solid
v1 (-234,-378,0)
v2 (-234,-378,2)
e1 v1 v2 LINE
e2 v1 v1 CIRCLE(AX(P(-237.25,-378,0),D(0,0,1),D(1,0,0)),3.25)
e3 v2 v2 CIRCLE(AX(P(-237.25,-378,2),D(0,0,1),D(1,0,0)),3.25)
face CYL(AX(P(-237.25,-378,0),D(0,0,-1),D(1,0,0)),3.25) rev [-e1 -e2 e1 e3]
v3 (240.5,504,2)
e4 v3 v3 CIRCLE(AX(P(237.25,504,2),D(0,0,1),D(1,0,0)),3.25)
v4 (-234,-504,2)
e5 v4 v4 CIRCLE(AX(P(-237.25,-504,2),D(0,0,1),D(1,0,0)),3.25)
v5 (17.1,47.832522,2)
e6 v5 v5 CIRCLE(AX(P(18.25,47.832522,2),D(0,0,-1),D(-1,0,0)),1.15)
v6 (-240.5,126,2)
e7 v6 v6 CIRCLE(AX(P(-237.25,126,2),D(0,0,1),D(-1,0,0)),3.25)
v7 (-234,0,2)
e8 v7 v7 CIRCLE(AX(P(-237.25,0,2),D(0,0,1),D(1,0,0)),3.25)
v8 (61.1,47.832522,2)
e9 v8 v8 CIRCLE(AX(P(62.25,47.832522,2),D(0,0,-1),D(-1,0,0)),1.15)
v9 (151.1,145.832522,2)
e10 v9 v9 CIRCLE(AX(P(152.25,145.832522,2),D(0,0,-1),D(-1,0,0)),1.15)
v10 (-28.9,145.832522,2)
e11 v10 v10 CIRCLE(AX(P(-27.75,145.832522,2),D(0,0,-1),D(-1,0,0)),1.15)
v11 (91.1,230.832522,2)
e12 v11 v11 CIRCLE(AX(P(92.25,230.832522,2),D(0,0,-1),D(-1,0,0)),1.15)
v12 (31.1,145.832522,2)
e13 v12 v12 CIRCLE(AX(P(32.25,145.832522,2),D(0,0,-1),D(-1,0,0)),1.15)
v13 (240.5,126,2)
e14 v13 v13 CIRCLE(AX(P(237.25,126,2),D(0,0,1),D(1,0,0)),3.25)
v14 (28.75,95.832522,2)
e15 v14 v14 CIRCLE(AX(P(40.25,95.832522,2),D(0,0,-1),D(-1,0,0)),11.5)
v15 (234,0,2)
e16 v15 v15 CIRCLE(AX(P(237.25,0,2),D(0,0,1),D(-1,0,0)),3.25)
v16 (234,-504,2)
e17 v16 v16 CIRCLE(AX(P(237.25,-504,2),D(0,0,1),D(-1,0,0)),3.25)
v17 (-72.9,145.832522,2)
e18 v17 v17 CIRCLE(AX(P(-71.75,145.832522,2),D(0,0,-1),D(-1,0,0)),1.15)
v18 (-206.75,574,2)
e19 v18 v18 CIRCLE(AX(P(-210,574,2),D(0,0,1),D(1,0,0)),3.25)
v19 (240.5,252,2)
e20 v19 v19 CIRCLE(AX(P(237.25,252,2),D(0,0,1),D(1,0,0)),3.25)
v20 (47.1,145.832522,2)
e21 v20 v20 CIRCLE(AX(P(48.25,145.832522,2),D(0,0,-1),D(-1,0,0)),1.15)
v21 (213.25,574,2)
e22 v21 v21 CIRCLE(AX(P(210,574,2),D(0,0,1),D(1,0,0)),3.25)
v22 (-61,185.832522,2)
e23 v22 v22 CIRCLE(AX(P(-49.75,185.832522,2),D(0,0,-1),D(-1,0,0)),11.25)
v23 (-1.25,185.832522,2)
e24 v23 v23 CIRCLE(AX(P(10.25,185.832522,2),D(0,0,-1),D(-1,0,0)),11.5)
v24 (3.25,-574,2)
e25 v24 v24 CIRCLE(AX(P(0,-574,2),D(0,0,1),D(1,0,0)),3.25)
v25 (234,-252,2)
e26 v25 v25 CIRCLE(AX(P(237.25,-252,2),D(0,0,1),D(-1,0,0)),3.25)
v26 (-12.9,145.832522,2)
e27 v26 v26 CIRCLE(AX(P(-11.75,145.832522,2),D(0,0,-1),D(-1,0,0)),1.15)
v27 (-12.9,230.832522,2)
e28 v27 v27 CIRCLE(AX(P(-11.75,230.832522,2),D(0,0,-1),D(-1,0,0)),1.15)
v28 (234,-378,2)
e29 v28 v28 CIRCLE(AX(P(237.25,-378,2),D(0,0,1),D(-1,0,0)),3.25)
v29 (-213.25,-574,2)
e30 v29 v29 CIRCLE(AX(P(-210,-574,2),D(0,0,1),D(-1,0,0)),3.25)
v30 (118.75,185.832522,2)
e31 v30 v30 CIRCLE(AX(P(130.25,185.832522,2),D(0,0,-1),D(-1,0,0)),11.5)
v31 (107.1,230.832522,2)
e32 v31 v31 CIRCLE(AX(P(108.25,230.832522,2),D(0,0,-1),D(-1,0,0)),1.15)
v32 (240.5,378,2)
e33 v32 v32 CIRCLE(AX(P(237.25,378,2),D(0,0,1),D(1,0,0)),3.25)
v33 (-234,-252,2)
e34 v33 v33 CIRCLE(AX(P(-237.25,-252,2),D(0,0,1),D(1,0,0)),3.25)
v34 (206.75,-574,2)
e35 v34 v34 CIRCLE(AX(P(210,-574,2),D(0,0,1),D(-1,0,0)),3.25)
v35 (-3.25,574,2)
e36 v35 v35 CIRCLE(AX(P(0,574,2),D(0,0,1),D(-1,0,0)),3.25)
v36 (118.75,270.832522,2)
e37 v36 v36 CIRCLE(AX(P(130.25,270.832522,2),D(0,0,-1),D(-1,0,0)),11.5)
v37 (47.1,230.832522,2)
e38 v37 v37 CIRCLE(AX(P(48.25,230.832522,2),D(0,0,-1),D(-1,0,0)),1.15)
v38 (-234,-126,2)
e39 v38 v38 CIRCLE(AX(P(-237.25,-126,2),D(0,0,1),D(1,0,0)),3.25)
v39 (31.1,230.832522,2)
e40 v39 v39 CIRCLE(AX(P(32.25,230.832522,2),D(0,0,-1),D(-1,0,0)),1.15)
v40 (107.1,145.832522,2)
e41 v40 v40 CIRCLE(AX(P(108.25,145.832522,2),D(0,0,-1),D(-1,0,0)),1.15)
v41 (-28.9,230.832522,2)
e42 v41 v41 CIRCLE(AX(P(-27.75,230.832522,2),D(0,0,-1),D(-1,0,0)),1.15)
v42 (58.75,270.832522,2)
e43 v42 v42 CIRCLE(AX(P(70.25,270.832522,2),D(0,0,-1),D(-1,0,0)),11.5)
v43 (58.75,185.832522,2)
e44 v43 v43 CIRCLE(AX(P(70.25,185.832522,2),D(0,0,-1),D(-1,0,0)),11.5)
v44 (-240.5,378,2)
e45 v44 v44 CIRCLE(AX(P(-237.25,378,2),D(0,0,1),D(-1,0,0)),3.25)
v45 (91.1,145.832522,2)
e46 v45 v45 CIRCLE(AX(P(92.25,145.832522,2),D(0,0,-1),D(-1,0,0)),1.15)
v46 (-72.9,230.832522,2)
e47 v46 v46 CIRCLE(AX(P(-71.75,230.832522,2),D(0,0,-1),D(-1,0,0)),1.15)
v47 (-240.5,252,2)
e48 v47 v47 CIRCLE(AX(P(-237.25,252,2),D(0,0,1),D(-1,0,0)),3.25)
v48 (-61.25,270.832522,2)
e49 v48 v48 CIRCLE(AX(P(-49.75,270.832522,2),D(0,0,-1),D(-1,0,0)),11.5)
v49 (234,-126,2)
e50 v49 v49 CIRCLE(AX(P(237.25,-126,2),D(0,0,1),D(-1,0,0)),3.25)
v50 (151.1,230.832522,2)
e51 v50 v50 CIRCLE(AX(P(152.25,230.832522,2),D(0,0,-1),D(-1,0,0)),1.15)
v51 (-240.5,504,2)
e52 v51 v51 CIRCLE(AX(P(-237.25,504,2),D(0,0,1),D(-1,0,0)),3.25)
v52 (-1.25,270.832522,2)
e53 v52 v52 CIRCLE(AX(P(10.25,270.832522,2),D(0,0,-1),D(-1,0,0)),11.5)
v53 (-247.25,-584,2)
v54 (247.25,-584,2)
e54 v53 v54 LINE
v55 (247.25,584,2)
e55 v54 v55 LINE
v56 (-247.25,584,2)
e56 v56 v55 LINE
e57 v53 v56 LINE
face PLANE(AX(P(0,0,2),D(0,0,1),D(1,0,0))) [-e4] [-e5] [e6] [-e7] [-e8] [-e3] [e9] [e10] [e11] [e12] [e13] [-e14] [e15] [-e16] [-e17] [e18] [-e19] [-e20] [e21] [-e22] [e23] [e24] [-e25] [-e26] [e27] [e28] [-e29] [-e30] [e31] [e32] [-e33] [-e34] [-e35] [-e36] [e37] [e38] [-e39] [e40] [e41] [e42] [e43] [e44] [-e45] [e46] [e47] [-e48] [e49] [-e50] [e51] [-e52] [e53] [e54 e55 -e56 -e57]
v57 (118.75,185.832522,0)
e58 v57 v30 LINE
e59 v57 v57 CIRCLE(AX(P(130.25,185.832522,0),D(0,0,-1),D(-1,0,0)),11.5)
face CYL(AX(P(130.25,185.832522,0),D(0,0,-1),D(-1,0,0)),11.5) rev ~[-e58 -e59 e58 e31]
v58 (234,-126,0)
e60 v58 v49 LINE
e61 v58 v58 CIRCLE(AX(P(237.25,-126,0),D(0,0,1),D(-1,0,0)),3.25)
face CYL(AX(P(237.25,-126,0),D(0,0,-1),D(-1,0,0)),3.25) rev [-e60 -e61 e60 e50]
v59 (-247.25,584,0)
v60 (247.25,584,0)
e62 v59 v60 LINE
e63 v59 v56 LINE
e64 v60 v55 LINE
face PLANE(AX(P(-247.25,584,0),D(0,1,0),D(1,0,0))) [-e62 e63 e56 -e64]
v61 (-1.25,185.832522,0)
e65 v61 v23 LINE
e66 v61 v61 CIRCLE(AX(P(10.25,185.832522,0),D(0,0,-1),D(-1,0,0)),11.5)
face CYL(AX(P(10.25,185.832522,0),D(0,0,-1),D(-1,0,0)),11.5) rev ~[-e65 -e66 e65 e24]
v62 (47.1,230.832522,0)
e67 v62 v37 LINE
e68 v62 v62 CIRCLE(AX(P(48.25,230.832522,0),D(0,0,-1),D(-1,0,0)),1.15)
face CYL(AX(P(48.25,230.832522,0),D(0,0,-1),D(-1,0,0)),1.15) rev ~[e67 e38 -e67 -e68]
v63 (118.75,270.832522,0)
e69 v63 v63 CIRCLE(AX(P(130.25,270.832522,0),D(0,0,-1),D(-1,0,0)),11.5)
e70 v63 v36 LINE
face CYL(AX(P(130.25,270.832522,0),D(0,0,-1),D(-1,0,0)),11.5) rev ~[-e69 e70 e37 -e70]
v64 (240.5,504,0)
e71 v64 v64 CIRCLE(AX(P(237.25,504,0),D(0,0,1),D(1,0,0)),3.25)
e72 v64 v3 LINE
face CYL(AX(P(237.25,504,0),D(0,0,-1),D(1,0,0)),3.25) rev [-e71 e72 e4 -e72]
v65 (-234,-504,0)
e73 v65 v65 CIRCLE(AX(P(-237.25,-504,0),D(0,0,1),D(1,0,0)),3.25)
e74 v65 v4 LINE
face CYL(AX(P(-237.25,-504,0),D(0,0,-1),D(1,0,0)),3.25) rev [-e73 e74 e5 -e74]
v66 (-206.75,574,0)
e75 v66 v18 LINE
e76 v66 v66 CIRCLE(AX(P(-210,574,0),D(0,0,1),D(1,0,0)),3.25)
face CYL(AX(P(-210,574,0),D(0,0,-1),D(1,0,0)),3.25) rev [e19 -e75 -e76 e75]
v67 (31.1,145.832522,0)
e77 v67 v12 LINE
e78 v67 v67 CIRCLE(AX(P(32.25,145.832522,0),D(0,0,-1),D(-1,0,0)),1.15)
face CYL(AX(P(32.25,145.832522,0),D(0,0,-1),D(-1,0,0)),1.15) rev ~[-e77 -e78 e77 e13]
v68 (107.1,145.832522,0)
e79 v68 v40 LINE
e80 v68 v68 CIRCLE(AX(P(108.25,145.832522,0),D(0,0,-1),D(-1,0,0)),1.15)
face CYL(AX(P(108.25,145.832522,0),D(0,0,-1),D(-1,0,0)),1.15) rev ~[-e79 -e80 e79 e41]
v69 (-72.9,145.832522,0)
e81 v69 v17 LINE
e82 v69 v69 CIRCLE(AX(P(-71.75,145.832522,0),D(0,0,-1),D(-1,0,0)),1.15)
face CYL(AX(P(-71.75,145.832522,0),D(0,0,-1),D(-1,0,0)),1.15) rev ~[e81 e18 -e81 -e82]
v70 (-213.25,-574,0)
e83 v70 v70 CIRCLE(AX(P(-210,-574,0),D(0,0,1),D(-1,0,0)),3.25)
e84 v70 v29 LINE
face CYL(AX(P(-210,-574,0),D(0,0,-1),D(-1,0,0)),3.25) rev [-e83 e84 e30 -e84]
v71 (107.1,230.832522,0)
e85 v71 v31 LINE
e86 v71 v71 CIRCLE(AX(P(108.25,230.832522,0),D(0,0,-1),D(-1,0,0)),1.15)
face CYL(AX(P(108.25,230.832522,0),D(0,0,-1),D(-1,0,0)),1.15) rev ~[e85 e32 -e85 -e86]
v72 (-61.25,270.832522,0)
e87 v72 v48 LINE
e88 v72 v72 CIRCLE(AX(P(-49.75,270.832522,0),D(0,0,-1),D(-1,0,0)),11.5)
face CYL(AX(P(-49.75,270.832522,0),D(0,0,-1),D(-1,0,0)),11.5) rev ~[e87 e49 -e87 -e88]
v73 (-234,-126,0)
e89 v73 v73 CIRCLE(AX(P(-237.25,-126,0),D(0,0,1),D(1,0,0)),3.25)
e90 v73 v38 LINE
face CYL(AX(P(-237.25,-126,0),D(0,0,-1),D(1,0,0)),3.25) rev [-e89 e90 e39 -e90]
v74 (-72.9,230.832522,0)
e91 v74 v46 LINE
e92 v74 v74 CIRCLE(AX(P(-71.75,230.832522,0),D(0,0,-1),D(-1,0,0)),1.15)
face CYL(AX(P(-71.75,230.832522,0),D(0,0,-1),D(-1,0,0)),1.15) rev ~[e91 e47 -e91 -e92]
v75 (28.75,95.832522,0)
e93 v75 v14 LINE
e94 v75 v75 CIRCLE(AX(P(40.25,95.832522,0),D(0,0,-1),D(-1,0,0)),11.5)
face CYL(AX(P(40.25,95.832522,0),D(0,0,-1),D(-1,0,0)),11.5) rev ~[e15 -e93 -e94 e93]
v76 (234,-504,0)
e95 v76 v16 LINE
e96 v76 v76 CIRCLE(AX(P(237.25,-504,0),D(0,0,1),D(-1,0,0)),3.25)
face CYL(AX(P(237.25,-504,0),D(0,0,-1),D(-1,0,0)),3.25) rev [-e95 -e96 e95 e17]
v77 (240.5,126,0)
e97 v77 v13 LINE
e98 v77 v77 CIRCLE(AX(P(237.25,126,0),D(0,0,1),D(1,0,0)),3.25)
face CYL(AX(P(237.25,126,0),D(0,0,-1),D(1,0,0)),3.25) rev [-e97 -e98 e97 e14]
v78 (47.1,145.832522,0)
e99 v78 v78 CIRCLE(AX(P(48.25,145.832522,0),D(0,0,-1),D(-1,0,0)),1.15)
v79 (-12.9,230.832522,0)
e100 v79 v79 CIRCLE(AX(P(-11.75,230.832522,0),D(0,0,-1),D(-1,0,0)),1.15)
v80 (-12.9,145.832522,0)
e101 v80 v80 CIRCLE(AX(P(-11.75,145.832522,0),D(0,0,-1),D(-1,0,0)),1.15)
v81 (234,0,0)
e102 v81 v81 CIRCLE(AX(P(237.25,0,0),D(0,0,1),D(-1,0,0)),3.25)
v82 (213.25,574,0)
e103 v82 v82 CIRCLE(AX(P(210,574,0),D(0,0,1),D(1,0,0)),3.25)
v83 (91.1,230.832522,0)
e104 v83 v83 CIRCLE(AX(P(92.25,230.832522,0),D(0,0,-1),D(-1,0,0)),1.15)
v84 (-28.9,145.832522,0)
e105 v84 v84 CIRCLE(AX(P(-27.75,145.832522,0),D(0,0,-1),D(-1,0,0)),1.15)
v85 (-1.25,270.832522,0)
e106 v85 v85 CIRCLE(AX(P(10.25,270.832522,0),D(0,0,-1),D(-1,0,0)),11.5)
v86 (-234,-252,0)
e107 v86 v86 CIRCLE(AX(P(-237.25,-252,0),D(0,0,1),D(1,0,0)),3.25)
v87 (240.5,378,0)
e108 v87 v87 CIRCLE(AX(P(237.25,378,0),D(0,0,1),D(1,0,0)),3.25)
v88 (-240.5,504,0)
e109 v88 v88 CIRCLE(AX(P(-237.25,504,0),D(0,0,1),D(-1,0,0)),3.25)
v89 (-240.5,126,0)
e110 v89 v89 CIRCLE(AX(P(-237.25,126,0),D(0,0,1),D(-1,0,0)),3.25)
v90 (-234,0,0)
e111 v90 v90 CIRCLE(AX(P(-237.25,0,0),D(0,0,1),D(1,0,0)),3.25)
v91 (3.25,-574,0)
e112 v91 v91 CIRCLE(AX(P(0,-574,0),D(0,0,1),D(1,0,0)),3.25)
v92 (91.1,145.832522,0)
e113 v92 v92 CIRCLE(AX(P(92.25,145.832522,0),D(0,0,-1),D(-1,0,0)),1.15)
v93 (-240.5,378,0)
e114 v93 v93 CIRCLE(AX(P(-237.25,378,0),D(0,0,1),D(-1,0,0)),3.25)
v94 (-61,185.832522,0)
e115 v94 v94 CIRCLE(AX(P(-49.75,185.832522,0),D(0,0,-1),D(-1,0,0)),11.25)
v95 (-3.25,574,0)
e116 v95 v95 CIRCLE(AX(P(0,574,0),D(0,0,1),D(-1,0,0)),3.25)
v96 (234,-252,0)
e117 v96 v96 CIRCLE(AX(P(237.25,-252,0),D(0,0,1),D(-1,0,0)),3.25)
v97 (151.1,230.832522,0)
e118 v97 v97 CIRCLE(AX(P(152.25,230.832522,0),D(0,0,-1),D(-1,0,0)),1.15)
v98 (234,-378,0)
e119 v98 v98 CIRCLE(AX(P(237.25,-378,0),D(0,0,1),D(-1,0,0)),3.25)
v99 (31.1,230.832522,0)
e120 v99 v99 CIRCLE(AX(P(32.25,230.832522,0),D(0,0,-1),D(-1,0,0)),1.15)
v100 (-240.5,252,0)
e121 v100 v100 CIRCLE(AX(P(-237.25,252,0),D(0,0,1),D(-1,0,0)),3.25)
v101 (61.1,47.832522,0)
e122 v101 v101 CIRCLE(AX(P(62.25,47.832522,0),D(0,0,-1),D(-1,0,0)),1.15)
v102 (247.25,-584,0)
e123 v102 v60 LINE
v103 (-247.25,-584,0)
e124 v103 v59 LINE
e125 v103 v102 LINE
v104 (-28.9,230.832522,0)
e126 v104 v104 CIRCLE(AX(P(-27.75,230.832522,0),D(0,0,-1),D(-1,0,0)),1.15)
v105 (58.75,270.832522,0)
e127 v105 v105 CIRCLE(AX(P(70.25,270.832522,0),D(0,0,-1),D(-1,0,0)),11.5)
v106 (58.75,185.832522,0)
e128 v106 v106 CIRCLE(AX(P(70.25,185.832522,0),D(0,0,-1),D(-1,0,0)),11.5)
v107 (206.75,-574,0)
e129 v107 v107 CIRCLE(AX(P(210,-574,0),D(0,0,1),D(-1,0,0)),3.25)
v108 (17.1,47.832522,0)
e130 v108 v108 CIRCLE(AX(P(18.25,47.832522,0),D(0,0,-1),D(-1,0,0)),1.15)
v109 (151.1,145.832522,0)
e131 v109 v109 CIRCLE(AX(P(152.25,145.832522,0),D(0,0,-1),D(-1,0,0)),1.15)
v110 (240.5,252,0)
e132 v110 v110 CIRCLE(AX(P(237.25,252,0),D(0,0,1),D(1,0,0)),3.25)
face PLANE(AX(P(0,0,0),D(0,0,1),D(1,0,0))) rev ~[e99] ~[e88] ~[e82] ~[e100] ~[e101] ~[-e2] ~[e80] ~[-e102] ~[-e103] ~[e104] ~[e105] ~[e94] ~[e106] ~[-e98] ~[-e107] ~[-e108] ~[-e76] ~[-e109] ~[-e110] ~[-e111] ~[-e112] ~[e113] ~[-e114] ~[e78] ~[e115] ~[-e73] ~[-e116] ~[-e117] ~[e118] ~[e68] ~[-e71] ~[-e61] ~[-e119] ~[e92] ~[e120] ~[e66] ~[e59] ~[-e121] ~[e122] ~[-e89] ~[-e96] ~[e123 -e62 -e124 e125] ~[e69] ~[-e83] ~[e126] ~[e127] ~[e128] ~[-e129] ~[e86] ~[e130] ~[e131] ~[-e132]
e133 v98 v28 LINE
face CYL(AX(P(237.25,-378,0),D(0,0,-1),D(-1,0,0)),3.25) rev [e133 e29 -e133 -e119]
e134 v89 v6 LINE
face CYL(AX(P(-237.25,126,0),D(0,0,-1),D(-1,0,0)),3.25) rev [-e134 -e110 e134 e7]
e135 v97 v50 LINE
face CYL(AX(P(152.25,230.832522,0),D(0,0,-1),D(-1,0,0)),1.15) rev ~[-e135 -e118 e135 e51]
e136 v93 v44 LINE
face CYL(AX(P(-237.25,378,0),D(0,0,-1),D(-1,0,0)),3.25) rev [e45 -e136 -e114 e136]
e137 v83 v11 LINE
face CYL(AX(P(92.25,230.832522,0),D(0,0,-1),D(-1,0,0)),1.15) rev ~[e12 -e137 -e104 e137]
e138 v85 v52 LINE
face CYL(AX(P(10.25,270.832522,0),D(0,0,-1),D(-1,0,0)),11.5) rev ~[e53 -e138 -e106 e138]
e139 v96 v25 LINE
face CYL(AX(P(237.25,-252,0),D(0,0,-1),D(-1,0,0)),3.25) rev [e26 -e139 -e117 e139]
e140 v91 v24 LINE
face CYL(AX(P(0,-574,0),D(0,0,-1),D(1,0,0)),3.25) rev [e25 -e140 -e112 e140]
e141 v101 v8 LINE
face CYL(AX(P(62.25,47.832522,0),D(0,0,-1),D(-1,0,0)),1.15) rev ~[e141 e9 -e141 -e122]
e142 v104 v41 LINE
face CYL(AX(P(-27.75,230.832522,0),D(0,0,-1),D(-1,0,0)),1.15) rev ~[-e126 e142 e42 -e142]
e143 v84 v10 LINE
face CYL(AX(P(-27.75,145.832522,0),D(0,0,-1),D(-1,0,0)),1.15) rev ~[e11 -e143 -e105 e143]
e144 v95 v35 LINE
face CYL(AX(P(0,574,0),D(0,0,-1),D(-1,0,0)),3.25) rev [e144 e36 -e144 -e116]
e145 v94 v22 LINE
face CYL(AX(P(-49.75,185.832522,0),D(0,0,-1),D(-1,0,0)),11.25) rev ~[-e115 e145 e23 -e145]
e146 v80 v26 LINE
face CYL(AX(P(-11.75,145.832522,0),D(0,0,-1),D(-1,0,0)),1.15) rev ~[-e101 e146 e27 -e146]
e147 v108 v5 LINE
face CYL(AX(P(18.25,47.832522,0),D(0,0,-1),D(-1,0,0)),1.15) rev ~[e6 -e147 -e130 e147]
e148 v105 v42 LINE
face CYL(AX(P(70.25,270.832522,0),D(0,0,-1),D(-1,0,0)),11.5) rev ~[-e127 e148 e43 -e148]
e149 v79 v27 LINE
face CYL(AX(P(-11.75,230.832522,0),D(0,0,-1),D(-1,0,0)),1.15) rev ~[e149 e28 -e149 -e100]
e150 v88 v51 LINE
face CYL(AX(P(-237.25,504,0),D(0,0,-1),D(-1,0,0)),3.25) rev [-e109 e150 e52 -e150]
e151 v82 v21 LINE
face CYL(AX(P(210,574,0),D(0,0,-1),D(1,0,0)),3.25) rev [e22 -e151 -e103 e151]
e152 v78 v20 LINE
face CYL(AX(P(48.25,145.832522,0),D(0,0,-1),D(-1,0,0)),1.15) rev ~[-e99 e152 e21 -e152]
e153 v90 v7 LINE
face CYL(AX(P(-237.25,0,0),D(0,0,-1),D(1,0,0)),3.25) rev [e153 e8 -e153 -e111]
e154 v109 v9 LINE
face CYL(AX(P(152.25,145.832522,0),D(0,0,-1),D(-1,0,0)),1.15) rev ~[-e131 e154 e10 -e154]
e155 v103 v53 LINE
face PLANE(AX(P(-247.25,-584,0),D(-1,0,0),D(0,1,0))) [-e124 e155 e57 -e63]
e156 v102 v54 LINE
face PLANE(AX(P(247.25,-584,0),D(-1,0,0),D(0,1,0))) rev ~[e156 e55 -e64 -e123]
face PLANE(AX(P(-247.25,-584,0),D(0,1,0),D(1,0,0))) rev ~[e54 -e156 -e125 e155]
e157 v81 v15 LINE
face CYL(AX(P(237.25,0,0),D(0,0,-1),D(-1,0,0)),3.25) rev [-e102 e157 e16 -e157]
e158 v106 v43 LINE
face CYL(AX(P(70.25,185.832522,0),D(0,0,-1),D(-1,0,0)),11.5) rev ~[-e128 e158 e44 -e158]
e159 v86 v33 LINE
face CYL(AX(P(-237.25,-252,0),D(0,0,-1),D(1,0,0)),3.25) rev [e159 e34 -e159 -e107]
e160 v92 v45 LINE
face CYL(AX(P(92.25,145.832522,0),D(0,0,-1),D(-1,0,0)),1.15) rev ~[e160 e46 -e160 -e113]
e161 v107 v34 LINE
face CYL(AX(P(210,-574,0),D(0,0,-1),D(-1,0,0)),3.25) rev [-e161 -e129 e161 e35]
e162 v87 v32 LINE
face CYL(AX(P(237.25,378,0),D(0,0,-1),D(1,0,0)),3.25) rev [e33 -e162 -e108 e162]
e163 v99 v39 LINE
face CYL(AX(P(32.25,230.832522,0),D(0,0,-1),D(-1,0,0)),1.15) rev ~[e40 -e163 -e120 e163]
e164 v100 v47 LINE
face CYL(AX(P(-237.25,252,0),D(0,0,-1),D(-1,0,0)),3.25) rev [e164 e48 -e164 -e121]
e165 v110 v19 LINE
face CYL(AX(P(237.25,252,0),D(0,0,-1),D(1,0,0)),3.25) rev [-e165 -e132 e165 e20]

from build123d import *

# Parameters (mm, degrees)
SKETCH_1_W          = 494.5
SKETCH_1_H          = 1168
SKETCH_1_R          = 3.25
EXTRUDE_1_DEPTH     = 2
SKETCH_3_R          = 1.15
SKETCH_3_R_2        = 11.5
SKETCH_3_R_3        = 11.25
CUT_EXTRUDE_2_DEPTH = 10


with BuildPart() as part:
    # 草图1 → 凸台-拉伸1 (new body)
    with BuildSketch(Plane.XY):
        Rectangle(SKETCH_1_W, SKETCH_1_H)
        with Locations((-237.25, 0)):
            Circle(SKETCH_1_R, mode=Mode.SUBTRACT)
        with Locations((-237.25, -126)):
            Circle(SKETCH_1_R, mode=Mode.SUBTRACT)
        with Locations((-237.25, -252)):
            Circle(SKETCH_1_R, mode=Mode.SUBTRACT)
        with Locations((-237.25, -378)):
            Circle(SKETCH_1_R, mode=Mode.SUBTRACT)
        with Locations((-237.25, -504)):
            Circle(SKETCH_1_R, mode=Mode.SUBTRACT)
        with Locations((0, -574)):
            Circle(SKETCH_1_R, mode=Mode.SUBTRACT)
        with Locations(Location((0, 574, 0), (0, 0, 180))):
            Circle(SKETCH_1_R, mode=Mode.SUBTRACT)
        with Locations(Location((-237.25, 504, 0), (0, 0, 180))):
            Circle(SKETCH_1_R, mode=Mode.SUBTRACT)
        with Locations(Location((-237.25, 378, 0), (0, 0, 180))):
            Circle(SKETCH_1_R, mode=Mode.SUBTRACT)
        with Locations(Location((-237.25, 252, 0), (0, 0, 180))):
            Circle(SKETCH_1_R, mode=Mode.SUBTRACT)
        with Locations(Location((-237.25, 126, 0), (0, 0, 180))):
            Circle(SKETCH_1_R, mode=Mode.SUBTRACT)
        with Locations((237.25, 126)):
            Circle(SKETCH_1_R, mode=Mode.SUBTRACT)
        with Locations((237.25, 252)):
            Circle(SKETCH_1_R, mode=Mode.SUBTRACT)
        with Locations((237.25, 378)):
            Circle(SKETCH_1_R, mode=Mode.SUBTRACT)
        with Locations((237.25, 504)):
            Circle(SKETCH_1_R, mode=Mode.SUBTRACT)
        with Locations(Location((237.25, -504, 0), (0, 0, 180))):
            Circle(SKETCH_1_R, mode=Mode.SUBTRACT)
        with Locations(Location((237.25, -378, 0), (0, 0, 180))):
            Circle(SKETCH_1_R, mode=Mode.SUBTRACT)
        with Locations(Location((237.25, -252, 0), (0, 0, 180))):
            Circle(SKETCH_1_R, mode=Mode.SUBTRACT)
        with Locations(Location((237.25, -126, 0), (0, 0, 180))):
            Circle(SKETCH_1_R, mode=Mode.SUBTRACT)
        with Locations(Location((237.25, 0, 0), (0, 0, 180))):
            Circle(SKETCH_1_R, mode=Mode.SUBTRACT)
        with Locations((-210, 574)):
            Circle(SKETCH_1_R, mode=Mode.SUBTRACT)
        with Locations((210, 574)):
            Circle(SKETCH_1_R, mode=Mode.SUBTRACT)
        with Locations(Location((210, -574, 0), (0, 0, 180))):
            Circle(SKETCH_1_R, mode=Mode.SUBTRACT)
        with Locations(Location((-210, -574, 0), (0, 0, 180))):
            Circle(SKETCH_1_R, mode=Mode.SUBTRACT)
    extrude(amount=EXTRUDE_1_DEPTH)

    # 草图3 → 切除-拉伸2 (cut)
    with BuildSketch(Plane(origin=(0, 0, 0), x_dir=(-1, 0, 0), z_dir=(0, 0, -1))):
        with Locations((-48.25, 145.832522251)):
            Circle(SKETCH_3_R)
        with Locations((-10.25, 185.832522251)):
            Circle(SKETCH_3_R_2)
        with Locations((-32.25, 145.832522251)):
            Circle(SKETCH_3_R)
        with Locations((11.75, 145.832522251)):
            Circle(SKETCH_3_R)
        with Locations((27.75, 145.832522251)):
            Circle(SKETCH_3_R)
        with Locations((71.75, 145.832522251)):
            Circle(SKETCH_3_R)
        with Locations((49.75, 270.832522251)):
            Circle(SKETCH_3_R_2)
        with Locations((27.75, 230.832522251)):
            Circle(SKETCH_3_R)
        with Locations((71.75, 230.832522251)):
            Circle(SKETCH_3_R)
        with Locations((-130.25, 185.832522251)):
            Circle(SKETCH_3_R_2)
        with Locations((-152.25, 145.832522251)):
            Circle(SKETCH_3_R)
        with Locations((-108.25, 145.832522251)):
            Circle(SKETCH_3_R)
        with Locations((-70.25, 185.832522251)):
            Circle(SKETCH_3_R_2)
        with Locations((-92.25, 145.832522251)):
            Circle(SKETCH_3_R)
        with Locations((-152.25, 230.832522251)):
            Circle(SKETCH_3_R)
        with Locations((-108.25, 230.832522251)):
            Circle(SKETCH_3_R)
        with Locations((-70.25, 270.832522251)):
            Circle(SKETCH_3_R_2)
        with Locations((-92.25, 230.832522251)):
            Circle(SKETCH_3_R)
        with Locations((-48.25, 230.832522251)):
            Circle(SKETCH_3_R)
        with Locations((-10.25, 270.832522251)):
            Circle(SKETCH_3_R_2)
        with Locations((-32.25, 230.832522251)):
            Circle(SKETCH_3_R)
        with Locations((11.75, 230.832522251)):
            Circle(SKETCH_3_R)
        with Locations((-40.25, 95.832522251)):
            Circle(SKETCH_3_R_2)
        with Locations((-62.25, 47.832522251)):
            Circle(SKETCH_3_R)
        with Locations((-18.25, 47.832522251)):
            Circle(SKETCH_3_R)
        with Locations((-130.25, 270.832522251)):
            Circle(SKETCH_3_R_2)
        with Locations((49.75, 185.832522251)):
            Circle(SKETCH_3_R_3)
    extrude(amount=-CUT_EXTRUDE_2_DEPTH, mode=Mode.SUBTRACT)


solid = part.part
